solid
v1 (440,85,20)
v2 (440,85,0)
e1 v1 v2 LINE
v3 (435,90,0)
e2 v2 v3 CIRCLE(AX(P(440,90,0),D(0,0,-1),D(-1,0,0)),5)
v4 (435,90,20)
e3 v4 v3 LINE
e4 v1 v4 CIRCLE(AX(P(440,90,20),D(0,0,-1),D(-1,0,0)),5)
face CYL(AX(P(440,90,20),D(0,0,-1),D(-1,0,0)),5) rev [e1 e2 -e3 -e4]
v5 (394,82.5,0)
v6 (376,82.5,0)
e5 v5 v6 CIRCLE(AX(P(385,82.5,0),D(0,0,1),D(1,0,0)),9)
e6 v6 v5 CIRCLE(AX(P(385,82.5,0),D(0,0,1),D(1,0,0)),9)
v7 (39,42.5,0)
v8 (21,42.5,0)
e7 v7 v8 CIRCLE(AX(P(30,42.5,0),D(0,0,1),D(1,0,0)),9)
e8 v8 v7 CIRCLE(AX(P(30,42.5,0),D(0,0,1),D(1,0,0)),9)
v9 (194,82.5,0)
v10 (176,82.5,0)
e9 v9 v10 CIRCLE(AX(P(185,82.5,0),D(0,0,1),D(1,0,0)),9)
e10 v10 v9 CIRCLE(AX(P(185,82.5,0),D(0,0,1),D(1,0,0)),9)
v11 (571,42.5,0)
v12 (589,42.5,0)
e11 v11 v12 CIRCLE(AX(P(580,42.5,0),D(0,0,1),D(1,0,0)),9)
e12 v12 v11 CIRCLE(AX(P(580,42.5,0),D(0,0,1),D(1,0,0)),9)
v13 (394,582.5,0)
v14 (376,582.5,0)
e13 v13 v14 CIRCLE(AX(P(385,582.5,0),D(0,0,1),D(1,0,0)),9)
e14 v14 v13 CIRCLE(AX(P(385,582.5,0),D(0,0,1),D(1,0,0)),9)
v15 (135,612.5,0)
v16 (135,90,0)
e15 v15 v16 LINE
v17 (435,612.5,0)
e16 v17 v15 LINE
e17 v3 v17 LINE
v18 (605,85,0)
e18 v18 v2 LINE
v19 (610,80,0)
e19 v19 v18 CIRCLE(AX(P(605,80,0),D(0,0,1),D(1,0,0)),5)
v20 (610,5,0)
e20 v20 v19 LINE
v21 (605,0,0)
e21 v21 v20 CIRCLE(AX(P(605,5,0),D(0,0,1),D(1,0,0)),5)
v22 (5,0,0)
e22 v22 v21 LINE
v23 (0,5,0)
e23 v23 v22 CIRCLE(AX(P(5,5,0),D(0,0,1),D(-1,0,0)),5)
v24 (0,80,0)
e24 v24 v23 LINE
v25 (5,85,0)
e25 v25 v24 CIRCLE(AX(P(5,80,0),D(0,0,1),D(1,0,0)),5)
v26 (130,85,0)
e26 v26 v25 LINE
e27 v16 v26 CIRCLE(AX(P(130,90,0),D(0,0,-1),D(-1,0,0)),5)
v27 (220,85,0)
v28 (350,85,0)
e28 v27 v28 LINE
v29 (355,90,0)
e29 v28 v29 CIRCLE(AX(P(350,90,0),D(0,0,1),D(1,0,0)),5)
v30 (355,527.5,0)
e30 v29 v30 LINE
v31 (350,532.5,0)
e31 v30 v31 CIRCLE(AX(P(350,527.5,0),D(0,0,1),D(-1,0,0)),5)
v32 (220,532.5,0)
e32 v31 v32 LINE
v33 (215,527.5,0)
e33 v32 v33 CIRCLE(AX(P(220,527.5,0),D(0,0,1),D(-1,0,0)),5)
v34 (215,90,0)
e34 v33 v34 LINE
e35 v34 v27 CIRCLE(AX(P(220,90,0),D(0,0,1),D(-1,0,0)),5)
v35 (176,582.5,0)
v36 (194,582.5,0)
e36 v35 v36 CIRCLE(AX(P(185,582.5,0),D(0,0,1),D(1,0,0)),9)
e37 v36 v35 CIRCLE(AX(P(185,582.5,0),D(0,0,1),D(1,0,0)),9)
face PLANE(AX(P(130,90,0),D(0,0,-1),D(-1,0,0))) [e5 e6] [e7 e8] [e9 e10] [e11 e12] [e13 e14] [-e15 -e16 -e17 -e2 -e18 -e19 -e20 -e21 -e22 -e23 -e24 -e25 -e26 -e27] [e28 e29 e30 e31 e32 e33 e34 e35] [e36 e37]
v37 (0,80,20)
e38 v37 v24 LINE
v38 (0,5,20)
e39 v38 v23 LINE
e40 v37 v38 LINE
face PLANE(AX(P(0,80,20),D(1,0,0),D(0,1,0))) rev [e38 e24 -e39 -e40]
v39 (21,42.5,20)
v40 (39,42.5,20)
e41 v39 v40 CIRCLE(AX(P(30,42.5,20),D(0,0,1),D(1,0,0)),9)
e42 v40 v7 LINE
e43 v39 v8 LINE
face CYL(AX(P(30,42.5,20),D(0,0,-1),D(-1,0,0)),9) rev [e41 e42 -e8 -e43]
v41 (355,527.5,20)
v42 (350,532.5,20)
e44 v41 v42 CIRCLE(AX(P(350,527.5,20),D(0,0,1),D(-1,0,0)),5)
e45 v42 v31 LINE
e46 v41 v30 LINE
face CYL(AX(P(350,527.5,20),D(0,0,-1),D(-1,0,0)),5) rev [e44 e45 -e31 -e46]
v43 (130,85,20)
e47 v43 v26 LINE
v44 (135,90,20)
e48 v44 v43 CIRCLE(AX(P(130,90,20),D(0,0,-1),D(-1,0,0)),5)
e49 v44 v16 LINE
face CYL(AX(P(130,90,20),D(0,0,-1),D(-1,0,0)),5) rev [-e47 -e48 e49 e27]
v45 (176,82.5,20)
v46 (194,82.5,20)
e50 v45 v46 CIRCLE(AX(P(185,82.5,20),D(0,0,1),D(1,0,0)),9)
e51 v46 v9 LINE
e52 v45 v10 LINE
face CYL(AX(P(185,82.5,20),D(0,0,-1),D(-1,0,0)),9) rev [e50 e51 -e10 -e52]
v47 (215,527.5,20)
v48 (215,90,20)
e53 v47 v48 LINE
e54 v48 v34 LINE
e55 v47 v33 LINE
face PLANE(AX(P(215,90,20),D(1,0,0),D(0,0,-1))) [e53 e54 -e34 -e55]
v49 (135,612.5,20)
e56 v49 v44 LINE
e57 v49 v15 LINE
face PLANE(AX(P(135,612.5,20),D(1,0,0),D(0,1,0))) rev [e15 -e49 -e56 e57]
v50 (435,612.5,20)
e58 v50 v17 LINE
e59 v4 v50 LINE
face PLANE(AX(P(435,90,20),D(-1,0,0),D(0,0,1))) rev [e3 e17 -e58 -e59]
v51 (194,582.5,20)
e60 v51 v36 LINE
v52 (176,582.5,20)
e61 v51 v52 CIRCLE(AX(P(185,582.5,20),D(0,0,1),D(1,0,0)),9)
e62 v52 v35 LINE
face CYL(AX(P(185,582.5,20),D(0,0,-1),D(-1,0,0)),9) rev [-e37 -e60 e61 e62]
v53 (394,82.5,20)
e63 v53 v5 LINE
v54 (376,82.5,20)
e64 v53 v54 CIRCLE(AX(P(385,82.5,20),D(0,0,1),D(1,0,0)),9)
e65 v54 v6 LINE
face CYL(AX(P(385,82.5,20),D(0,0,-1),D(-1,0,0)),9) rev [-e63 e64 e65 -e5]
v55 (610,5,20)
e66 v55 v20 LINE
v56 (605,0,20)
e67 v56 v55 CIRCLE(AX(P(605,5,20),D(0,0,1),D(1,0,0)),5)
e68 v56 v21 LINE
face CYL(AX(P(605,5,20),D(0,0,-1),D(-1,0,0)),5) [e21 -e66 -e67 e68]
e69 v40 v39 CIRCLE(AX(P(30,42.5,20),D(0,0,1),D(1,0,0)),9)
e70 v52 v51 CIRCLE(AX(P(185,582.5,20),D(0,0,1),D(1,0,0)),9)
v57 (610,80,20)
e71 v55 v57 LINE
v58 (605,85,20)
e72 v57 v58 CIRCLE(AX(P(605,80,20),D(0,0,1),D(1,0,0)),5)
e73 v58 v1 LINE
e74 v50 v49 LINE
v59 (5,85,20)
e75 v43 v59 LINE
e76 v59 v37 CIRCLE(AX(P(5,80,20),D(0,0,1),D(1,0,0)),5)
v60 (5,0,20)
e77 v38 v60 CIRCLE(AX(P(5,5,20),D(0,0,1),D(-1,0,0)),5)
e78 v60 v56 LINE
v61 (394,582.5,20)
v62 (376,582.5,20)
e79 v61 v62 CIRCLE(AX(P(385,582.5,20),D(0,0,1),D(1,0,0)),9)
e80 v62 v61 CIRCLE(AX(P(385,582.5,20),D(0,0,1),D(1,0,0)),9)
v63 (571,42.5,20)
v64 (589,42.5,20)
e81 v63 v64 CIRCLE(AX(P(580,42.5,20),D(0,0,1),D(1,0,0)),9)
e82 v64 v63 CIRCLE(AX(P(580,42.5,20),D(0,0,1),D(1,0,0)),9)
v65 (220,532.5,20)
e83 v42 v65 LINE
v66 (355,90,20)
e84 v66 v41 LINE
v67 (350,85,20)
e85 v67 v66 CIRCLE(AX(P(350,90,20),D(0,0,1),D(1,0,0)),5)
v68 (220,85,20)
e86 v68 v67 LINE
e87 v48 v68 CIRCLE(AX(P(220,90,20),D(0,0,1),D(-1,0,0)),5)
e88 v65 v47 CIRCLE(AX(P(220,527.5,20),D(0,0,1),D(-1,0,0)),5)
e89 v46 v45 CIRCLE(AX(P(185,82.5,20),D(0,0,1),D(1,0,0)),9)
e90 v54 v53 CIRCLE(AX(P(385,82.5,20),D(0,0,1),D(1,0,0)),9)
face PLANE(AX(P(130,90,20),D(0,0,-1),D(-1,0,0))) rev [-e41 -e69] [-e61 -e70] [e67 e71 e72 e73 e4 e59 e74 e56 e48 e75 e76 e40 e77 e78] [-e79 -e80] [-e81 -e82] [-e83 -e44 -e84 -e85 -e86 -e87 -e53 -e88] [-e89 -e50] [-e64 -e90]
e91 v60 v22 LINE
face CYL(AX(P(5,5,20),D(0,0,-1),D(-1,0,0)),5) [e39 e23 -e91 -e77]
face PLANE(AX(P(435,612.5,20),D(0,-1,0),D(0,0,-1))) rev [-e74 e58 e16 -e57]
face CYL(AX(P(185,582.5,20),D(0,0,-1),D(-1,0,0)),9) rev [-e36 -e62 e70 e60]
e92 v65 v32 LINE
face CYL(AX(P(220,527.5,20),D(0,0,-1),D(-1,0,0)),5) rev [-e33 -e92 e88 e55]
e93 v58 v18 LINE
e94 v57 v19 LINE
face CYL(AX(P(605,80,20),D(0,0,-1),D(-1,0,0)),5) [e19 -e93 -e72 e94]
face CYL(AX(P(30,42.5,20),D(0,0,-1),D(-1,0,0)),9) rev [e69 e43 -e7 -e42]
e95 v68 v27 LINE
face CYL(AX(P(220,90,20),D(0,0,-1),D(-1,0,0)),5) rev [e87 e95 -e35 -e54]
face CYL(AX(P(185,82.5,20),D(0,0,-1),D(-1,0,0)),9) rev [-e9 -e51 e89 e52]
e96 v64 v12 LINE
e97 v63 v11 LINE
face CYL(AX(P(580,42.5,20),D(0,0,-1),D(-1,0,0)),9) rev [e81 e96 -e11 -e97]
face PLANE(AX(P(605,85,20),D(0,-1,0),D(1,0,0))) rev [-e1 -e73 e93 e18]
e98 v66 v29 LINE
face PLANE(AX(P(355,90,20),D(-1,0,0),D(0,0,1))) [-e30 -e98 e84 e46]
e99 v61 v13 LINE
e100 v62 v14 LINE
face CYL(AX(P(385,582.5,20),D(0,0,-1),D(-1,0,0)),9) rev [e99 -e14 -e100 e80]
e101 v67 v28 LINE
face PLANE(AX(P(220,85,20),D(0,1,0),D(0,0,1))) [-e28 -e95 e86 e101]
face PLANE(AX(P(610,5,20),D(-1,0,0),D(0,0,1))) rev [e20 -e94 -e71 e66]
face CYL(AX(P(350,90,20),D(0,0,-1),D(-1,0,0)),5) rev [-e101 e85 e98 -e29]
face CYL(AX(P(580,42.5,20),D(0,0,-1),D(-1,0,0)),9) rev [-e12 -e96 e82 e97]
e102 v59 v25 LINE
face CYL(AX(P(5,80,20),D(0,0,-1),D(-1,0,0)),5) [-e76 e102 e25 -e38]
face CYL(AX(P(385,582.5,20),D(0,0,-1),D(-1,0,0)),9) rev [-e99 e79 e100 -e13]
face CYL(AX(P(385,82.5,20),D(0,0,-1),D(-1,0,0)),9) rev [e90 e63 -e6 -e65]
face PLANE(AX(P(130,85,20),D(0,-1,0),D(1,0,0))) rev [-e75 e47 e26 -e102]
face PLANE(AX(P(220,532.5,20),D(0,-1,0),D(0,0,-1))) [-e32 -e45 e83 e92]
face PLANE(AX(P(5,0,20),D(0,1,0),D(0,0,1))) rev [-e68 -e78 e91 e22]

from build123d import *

# Parameters (mm, degrees)
SKETCH1_R           = 9
BOSS_EXTRUDE1_DEPTH = 20


with BuildPart() as part:
    # Sketch1 → Boss-Extrude1 (new body)
    with BuildSketch(Plane.XY):
        with BuildLine():
            Line((5, 0), (605, 0))
            ThreePointArc((605, 0), (608.535533906, 1.464466094), (610, 5))
            Line((610, 5), (610, 80))
            ThreePointArc((610, 80), (608.535533906, 83.535533906), (605, 85))
            Line((605, 85), (440, 85))
            ThreePointArc((440, 85), (436.464466094, 86.464466094), (435, 90))
            Line((435, 90), (435, 612.5))
            Line((435, 612.5), (135, 612.5))
            Line((135, 612.5), (135, 90))
            ThreePointArc((135, 90), (133.535533906, 86.464466094), (130, 85))
            Line((130, 85), (5, 85))
            ThreePointArc((5, 85), (1.464466094, 83.535533906), (0, 80))
            Line((0, 80), (0, 5))
            ThreePointArc((0, 5), (1.464466094, 1.464466094), (5, 0))
        make_face()
        with Locations((30, 42.5)):
            Circle(SKETCH1_R, mode=Mode.SUBTRACT)
        with Locations((580, 42.5)):
            Circle(SKETCH1_R, mode=Mode.SUBTRACT)
        with Locations((185, 582.5)):
            Circle(SKETCH1_R, mode=Mode.SUBTRACT)
        with Locations((385, 582.5)):
            Circle(SKETCH1_R, mode=Mode.SUBTRACT)
        with Locations((185, 82.5)):
            Circle(SKETCH1_R, mode=Mode.SUBTRACT)
        with Locations((385, 82.5)):
            Circle(SKETCH1_R, mode=Mode.SUBTRACT)
        with BuildLine():
            Line((220, 85), (350, 85))
            ThreePointArc((350, 85), (353.535533906, 86.464466094), (355, 90))
            Line((355, 90), (355, 527.5))
            ThreePointArc((355, 527.5), (353.535533906, 531.035533906), (350, 532.5))
            Line((350, 532.5), (220, 532.5))
            ThreePointArc((220, 532.5), (216.464466094, 531.035533906), (215, 527.5))
            Line((215, 527.5), (215, 90))
            ThreePointArc((215, 90), (216.464466094, 86.464466094), (220, 85))
        make_face(mode=Mode.SUBTRACT)
    extrude(amount=BOSS_EXTRUDE1_DEPTH)


solid = part.part
